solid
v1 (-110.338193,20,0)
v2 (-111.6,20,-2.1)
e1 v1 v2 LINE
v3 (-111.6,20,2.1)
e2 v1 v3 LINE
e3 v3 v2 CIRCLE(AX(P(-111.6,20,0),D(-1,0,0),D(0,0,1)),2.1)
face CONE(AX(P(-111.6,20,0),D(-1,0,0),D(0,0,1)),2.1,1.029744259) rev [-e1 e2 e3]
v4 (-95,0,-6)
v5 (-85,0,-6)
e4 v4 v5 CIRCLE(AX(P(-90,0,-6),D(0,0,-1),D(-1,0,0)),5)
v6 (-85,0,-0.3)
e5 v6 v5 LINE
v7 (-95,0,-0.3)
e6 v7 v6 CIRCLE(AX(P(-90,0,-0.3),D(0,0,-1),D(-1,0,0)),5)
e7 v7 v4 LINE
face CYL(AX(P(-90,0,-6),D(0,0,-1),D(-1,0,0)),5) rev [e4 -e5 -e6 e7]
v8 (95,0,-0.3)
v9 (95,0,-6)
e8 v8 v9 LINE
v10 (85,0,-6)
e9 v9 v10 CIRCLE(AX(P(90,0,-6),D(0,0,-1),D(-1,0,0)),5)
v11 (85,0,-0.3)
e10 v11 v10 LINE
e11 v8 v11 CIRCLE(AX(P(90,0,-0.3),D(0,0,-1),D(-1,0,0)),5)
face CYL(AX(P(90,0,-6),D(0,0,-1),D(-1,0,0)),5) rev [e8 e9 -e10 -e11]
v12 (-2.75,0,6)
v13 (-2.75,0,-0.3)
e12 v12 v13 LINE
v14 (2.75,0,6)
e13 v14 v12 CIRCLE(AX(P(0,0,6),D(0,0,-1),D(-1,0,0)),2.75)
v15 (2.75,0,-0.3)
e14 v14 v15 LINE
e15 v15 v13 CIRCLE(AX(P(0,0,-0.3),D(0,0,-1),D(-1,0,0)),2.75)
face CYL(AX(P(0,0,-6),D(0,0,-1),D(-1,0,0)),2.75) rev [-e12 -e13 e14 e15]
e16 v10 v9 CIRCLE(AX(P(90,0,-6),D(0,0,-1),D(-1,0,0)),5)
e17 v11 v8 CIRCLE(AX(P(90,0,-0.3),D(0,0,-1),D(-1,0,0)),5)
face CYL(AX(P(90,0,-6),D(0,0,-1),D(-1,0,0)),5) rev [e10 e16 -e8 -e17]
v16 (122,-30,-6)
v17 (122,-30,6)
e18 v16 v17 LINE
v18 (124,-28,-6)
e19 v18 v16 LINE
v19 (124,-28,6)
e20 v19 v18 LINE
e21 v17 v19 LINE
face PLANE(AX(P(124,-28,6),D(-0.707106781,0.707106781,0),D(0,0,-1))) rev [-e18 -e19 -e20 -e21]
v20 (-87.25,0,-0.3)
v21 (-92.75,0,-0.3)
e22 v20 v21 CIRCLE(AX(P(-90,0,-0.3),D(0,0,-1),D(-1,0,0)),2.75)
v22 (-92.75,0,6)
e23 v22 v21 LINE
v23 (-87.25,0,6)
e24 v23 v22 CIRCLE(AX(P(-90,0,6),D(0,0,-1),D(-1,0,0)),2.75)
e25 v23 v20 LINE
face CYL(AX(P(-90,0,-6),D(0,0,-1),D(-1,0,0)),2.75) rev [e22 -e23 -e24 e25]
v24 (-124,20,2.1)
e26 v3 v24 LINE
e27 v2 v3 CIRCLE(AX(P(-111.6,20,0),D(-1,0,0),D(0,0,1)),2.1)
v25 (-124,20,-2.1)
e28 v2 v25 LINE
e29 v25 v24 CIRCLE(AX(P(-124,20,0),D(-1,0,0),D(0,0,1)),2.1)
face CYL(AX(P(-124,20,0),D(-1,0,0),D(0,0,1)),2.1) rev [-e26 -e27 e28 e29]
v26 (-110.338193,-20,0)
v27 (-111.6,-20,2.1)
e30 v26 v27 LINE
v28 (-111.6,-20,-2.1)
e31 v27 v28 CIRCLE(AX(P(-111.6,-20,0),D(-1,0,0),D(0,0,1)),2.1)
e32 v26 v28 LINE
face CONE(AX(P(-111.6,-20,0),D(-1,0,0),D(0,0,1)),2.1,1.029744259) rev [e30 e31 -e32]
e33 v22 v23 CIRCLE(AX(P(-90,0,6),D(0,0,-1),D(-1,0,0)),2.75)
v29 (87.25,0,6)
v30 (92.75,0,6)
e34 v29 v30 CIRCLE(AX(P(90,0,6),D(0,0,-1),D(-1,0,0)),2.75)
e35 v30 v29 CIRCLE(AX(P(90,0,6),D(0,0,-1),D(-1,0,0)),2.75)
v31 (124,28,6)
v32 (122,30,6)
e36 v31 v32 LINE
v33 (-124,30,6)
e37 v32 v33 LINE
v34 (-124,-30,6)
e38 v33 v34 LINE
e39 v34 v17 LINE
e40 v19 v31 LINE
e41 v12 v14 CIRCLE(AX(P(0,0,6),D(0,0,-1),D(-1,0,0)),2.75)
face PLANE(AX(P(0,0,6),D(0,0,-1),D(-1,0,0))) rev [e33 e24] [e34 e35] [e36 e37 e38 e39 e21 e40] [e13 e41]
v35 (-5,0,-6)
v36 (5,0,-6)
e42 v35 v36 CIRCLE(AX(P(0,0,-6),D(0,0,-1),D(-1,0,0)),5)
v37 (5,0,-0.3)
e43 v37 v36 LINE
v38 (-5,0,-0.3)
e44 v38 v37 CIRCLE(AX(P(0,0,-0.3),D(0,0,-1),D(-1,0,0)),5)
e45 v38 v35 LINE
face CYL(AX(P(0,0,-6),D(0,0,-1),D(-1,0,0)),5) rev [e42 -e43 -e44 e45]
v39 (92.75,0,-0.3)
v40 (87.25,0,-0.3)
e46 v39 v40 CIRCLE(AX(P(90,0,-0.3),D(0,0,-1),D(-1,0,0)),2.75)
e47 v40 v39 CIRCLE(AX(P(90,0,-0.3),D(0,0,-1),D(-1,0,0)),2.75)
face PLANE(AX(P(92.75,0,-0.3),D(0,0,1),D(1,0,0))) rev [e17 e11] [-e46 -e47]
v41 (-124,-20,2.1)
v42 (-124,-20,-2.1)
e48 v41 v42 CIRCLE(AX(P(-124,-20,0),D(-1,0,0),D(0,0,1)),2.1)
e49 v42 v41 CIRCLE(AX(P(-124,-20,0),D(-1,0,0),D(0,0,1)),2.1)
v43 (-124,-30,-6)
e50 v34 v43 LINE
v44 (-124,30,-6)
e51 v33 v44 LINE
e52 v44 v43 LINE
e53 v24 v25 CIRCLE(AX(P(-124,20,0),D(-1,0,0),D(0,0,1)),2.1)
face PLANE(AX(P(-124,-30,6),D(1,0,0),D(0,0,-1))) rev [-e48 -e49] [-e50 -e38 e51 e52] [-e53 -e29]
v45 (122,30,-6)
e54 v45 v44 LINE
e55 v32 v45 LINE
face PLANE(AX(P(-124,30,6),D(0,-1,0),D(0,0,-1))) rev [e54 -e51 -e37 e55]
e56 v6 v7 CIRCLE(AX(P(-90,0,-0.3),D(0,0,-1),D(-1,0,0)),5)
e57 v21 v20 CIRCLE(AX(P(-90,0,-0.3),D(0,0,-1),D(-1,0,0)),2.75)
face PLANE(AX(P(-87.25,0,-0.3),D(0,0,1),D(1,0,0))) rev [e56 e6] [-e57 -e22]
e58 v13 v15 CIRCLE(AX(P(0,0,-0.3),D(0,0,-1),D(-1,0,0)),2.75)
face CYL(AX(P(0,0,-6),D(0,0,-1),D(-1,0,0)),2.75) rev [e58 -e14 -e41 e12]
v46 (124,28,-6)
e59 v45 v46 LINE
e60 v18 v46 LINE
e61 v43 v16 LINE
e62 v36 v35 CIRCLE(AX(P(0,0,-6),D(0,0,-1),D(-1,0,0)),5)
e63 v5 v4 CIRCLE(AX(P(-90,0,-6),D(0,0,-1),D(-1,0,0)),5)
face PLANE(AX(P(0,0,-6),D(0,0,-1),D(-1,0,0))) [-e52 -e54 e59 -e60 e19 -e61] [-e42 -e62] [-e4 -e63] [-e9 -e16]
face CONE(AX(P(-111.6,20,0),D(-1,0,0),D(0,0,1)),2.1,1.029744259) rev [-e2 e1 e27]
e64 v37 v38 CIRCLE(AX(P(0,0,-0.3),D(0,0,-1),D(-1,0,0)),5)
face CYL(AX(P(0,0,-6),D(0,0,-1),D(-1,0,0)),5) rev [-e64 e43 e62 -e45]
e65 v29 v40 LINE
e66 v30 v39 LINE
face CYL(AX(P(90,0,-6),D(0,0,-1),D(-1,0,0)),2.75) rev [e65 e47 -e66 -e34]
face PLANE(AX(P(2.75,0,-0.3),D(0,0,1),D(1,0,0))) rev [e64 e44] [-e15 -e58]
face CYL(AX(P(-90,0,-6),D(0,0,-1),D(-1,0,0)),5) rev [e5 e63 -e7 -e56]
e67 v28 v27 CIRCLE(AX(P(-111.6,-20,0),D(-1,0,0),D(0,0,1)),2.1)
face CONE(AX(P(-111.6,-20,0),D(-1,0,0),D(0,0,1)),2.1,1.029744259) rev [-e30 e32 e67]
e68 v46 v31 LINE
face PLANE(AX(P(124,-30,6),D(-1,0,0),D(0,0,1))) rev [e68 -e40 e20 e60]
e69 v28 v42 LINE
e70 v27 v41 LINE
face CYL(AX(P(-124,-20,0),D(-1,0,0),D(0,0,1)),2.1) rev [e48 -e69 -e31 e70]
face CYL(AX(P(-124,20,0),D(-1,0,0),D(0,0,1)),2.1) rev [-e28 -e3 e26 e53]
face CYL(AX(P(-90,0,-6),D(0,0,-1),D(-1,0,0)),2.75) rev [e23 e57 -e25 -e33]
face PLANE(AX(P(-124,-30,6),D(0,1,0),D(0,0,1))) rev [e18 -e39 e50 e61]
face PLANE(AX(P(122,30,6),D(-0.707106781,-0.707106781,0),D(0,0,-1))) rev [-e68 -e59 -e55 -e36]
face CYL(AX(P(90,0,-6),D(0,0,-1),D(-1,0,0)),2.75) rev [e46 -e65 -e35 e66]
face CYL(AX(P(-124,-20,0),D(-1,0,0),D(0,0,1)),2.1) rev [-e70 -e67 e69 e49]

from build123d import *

# Parameters (mm, degrees)
SKETCH_1_W                     = 248
SKETCH_1_H                     = 60
EXTRUDE_1_DEPTH                = 6
HOLE_WIZARD_M5_1_D             = 4.2
HOLE_WIZARD_M5_1_DEPTH         = 12.4
HOLE_WIZARD_M5_1_TIP           = 1.2618073
CHAMFER_1_SIZE                 = 2
HOLE_WIZARD_M5_1_2_D           = 5.5
HOLE_WIZARD_M5_1_2_DEPTH       = 12.4
HOLE_WIZARD_M5_1_2_CBORE_D     = 10
HOLE_WIZARD_M5_1_2_CBORE_DEPTH = 5.7
HOLE_WIZARD_M5_1_2_TIP         = 1.652366702


with BuildPart() as part:
    # 草图1 → 凸台-拉伸1 (new, symmetric)
    with BuildSketch(Plane.XY):
        Rectangle(SKETCH_1_W, SKETCH_1_H)
    extrude(amount=EXTRUDE_1_DEPTH, both=True)

    # Hole Wizard M5 _1
    with Locations(Plane.ZY.offset(124)):
        with Locations((0, 20), (0, -20)):
            Hole(HOLE_WIZARD_M5_1_D / 2, depth=HOLE_WIZARD_M5_1_DEPTH)
            with Locations((0, 0, -(HOLE_WIZARD_M5_1_DEPTH + HOLE_WIZARD_M5_1_TIP / 2))):  # 118° drill point
                Cone(0, HOLE_WIZARD_M5_1_D / 2, HOLE_WIZARD_M5_1_TIP, mode=Mode.SUBTRACT)

    # 倒角1
    chamfer_1_edges = [part.edges().sort_by_distance(p)[0] for p in [
        (124, -30, 0),
        (124, 30, 0),
    ]]
    chamfer(chamfer_1_edges, length=CHAMFER_1_SIZE)

    # Hole Wizard M5 _1 2
    with Locations(Plane(origin=(0, 0, -6), x_dir=(-1, 0, 0), z_dir=(0, 0, -1))):
        with Locations((-90, 0), (0, 0), (90, 0)):
            CounterBoreHole(HOLE_WIZARD_M5_1_2_D / 2, HOLE_WIZARD_M5_1_2_CBORE_D / 2, HOLE_WIZARD_M5_1_2_CBORE_DEPTH, depth=HOLE_WIZARD_M5_1_2_DEPTH)
            with Locations((0, 0, -(HOLE_WIZARD_M5_1_2_DEPTH + HOLE_WIZARD_M5_1_2_TIP / 2))):  # 118° drill point
                Cone(0, HOLE_WIZARD_M5_1_2_D / 2, HOLE_WIZARD_M5_1_2_TIP, mode=Mode.SUBTRACT)


solid = part.part
